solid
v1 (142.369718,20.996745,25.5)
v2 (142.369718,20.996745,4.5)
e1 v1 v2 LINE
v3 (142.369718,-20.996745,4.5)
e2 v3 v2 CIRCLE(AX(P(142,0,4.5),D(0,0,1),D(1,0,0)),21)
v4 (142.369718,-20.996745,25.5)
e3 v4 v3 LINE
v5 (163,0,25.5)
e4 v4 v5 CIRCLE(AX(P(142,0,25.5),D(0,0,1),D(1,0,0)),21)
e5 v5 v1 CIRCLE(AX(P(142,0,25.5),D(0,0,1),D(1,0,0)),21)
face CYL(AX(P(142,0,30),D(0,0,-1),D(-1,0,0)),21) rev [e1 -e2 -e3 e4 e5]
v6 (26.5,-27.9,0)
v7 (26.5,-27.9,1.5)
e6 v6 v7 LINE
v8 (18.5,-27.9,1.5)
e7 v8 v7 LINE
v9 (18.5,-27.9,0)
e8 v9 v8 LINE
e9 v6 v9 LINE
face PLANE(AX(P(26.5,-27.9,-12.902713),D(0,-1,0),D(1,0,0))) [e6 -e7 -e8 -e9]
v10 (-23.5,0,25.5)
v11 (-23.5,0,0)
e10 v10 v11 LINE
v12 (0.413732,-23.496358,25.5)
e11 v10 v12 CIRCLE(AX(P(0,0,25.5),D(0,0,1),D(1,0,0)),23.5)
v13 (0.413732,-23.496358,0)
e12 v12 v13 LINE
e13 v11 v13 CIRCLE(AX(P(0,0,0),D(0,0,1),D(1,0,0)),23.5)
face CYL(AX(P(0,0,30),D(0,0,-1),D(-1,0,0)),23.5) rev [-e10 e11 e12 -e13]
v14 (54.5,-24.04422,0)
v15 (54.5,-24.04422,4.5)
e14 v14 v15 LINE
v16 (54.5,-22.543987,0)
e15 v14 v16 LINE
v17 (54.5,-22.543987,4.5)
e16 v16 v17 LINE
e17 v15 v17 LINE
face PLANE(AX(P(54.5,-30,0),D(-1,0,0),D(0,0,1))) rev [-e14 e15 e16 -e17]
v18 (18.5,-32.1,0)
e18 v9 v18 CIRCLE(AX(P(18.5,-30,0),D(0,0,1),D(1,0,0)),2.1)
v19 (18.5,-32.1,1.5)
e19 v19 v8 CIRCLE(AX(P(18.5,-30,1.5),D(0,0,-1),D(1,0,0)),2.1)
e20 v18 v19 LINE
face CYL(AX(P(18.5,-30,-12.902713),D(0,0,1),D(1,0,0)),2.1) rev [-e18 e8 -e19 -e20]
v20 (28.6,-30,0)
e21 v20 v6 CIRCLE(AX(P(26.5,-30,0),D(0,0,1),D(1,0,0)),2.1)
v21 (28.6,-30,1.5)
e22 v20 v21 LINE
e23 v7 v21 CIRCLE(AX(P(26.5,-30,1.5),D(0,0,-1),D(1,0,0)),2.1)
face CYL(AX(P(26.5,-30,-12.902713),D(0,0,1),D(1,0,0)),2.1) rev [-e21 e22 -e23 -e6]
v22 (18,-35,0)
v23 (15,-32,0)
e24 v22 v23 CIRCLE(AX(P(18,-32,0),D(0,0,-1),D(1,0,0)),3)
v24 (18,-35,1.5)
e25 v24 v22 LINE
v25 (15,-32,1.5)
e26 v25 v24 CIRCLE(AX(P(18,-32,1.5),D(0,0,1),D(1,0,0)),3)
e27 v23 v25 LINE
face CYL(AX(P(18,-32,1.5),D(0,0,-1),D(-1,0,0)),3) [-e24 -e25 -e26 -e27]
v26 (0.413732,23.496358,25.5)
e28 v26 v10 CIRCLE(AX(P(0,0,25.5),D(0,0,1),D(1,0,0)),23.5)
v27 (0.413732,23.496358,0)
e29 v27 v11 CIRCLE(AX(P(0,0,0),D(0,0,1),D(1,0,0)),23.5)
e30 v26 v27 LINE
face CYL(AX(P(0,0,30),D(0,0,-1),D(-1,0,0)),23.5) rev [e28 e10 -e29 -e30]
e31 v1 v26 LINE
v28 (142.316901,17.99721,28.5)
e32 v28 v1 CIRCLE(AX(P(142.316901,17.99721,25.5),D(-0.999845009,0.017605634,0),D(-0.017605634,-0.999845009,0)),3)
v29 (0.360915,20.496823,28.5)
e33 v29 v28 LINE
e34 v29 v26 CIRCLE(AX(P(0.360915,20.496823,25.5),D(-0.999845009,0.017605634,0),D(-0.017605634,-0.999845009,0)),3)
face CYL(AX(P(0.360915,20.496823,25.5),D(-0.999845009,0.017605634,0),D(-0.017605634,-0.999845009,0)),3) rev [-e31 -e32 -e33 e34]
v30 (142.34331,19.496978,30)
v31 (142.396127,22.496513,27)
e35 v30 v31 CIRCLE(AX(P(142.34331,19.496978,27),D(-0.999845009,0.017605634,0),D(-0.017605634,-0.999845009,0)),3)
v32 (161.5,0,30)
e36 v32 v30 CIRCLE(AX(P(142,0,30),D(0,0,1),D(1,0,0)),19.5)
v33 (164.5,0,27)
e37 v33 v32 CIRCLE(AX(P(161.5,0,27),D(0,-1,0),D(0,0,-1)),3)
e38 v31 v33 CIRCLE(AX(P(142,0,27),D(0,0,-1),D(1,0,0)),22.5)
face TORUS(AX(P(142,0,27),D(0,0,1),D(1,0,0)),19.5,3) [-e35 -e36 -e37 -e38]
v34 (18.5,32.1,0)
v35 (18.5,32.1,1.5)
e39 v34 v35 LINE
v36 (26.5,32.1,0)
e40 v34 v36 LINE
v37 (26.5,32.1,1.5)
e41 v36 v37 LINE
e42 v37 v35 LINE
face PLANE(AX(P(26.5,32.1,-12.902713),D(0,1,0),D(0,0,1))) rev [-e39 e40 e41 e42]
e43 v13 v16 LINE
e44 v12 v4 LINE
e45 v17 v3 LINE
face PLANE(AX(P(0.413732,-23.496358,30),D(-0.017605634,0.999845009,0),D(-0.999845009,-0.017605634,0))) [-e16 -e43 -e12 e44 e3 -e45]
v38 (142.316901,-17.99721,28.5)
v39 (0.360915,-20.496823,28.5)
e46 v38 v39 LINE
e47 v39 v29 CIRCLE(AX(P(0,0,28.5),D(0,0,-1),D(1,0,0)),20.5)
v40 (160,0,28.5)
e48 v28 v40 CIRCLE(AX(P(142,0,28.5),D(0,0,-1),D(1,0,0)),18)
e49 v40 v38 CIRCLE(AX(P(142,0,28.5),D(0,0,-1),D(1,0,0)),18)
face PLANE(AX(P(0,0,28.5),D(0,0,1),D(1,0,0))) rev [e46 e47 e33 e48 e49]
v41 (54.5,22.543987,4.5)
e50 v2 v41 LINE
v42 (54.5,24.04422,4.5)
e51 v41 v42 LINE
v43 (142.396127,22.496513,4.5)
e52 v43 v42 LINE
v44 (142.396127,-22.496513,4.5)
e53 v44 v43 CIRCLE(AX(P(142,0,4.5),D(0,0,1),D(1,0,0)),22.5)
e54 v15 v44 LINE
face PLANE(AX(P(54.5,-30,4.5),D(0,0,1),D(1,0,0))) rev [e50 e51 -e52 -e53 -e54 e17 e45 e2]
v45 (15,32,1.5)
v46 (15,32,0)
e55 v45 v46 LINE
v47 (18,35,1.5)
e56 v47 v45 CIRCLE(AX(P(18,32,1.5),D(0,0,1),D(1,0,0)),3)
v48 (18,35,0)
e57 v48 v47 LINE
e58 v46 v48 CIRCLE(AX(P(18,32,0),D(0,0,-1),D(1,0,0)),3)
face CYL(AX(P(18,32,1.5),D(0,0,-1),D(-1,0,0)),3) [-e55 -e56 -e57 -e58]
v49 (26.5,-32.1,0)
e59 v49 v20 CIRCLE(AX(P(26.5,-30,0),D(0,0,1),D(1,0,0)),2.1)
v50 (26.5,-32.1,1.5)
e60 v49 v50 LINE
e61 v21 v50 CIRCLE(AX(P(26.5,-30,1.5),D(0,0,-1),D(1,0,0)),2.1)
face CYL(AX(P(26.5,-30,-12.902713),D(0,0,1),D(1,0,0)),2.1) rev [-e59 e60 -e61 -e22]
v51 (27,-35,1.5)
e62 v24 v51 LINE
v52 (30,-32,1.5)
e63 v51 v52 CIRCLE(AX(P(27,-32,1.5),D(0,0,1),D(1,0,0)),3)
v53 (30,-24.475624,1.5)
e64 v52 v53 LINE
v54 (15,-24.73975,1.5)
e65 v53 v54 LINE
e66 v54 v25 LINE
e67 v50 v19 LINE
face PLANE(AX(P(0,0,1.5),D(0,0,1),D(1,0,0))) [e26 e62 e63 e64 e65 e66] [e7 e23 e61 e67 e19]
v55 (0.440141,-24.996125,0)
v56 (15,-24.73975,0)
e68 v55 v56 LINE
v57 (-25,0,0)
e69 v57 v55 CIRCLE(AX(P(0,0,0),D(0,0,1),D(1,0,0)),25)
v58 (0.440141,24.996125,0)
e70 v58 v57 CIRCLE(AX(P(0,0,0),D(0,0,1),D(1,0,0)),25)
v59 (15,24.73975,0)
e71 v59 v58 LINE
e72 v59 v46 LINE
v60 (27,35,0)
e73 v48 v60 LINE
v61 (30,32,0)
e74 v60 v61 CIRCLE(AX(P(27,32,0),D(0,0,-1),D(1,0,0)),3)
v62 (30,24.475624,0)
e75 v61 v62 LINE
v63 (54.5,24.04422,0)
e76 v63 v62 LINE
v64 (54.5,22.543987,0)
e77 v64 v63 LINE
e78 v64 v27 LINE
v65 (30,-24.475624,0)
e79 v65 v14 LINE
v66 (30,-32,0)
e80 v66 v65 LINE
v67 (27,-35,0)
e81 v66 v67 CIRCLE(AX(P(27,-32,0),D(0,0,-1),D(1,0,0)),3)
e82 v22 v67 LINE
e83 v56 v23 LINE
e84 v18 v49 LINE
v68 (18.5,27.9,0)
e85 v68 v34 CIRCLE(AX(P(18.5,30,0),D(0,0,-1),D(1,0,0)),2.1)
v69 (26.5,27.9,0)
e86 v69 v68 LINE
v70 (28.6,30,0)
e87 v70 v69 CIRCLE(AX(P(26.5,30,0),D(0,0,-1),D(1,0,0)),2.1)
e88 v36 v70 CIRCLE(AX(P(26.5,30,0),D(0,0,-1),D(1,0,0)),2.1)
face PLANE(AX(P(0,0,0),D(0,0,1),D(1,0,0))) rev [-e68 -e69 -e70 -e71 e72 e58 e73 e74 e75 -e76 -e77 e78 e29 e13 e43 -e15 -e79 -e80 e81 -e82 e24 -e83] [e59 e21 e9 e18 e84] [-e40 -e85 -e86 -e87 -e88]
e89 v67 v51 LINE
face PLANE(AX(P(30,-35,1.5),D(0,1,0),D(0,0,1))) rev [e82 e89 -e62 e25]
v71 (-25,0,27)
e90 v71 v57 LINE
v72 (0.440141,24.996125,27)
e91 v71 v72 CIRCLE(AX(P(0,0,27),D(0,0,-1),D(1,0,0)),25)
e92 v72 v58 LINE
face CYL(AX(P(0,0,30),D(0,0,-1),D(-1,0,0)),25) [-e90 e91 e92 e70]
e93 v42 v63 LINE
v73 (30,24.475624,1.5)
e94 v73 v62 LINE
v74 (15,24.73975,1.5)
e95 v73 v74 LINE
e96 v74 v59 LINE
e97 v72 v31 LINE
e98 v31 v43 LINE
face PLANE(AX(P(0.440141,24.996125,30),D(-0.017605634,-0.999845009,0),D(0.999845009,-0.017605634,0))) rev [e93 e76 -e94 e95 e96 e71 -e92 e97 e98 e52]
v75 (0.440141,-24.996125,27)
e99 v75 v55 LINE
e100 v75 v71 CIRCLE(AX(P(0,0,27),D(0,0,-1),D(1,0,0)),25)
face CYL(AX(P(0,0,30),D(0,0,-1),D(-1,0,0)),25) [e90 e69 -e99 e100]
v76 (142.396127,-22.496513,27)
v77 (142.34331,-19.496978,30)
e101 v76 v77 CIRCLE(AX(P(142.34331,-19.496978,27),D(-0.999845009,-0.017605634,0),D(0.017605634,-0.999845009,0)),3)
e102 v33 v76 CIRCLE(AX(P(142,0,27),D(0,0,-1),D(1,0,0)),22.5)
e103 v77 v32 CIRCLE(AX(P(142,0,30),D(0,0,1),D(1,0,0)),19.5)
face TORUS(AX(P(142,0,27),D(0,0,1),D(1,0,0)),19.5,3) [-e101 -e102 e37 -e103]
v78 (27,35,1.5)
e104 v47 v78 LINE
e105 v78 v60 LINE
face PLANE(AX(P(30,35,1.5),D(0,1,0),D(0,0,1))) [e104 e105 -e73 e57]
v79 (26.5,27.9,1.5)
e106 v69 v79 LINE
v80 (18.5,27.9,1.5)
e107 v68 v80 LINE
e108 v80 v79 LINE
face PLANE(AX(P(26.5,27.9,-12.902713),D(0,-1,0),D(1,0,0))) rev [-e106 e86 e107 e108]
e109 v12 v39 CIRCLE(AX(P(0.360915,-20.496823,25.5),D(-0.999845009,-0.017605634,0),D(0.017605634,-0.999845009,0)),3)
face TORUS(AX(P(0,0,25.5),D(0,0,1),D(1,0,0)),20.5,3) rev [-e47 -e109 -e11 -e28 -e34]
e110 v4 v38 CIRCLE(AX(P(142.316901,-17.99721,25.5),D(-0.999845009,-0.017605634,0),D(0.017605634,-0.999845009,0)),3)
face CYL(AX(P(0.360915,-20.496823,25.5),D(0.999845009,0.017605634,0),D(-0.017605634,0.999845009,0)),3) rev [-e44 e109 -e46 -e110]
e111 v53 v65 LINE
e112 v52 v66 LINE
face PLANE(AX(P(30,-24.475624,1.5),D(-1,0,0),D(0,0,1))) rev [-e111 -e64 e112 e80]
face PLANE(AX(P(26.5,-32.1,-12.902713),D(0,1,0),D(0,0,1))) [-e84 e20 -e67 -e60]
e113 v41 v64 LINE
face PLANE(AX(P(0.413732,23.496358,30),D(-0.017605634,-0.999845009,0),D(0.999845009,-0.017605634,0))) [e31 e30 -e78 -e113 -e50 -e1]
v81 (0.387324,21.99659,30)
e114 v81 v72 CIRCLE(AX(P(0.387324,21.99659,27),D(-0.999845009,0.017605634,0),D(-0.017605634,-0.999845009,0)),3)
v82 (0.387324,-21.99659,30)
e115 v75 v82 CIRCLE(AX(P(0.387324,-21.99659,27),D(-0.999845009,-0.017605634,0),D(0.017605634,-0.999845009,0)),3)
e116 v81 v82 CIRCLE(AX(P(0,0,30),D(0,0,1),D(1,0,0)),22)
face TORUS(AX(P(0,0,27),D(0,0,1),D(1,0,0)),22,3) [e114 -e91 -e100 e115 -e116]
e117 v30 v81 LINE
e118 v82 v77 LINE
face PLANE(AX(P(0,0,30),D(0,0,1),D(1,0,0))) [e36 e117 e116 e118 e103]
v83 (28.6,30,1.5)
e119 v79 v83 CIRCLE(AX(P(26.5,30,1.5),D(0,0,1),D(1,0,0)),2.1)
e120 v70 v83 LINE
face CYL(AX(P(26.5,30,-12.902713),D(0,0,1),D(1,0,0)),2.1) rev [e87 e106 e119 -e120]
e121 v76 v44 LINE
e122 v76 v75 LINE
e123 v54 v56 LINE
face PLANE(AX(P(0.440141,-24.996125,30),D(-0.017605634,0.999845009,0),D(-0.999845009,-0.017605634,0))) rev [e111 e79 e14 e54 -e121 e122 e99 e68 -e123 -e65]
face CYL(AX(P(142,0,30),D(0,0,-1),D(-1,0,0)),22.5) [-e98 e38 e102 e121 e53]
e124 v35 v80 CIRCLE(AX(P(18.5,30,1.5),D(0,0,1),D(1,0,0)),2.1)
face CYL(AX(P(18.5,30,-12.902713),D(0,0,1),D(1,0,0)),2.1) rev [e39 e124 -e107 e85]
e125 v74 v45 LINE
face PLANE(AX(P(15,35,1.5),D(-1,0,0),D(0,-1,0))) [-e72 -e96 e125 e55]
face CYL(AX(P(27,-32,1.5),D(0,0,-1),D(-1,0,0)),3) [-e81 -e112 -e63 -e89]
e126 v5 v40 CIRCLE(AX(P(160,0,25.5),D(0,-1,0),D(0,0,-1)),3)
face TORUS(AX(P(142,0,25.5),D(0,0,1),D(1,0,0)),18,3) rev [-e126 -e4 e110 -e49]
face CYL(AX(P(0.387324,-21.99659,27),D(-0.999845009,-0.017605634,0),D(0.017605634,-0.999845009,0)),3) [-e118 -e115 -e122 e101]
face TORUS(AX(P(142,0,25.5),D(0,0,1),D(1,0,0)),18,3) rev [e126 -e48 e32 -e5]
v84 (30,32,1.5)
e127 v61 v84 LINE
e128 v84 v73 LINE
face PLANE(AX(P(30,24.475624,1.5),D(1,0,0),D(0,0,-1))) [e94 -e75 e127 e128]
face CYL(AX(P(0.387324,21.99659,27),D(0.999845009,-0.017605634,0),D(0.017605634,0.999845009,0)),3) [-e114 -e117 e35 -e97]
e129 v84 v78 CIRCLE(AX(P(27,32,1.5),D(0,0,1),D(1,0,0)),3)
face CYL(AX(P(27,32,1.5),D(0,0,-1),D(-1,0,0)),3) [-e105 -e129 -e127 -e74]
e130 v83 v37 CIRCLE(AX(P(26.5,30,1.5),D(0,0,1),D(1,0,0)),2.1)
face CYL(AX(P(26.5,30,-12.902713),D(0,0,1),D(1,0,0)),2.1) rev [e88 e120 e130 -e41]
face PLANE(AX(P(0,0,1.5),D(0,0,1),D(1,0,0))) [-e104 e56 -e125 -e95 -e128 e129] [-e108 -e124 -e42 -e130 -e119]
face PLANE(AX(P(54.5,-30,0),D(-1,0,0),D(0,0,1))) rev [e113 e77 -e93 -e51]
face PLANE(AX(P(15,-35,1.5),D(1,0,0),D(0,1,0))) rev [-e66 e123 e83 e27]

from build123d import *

# Parameters (mm, degrees)
EXTRUDE_1_DEPTH     = 30
SHELL_1_T           = -1.5
EXTRUDE_2_DEPTH     = 1.5
CUT_EXTRUDE_1_DEPTH = 1.5
FILLET_1_R          = 3
SKETCH_4_W          = 110
SKETCH_4_H          = 4.5
CUT_EXTRUDE_2_DEPTH = 30


with BuildPart() as part:
    # 草图1 → 凸台-拉伸1 (new body)
    with BuildSketch(Plane.XY):
        with BuildLine():
            Line((0.440140845, 24.99612522), (142.396126761, 22.496512698))
            ThreePointArc((142.396126761, 22.496512698), (164.5, 0), (142.396126761, -22.496512698))
            Line((142.396126761, -22.496512698), (0.440140845, -24.99612522))
            ThreePointArc((0.440140845, -24.99612522), (-25, 0), (0.440140845, 24.99612522))
        make_face()
    extrude(amount=EXTRUDE_1_DEPTH)

    # 抽壳1
    shell_1_openings = [part.faces().sort_by_distance(p)[0] for p in [
        (68.129004911, 0, 0),
    ]]
    offset(amount=SHELL_1_T, openings=shell_1_openings, kind=Kind.INTERSECTION)

    # 草图2 → 凸台-拉伸2 (add)
    with BuildSketch(Plane(origin=(0, 0, 0), x_dir=(-1, 0, 0), z_dir=(0, 0, -1))):
        Polygon((-30, 24.475624492), (-30, 35), (-15, 35), (-15, 24.739749936), align=None)
    extrude_2 = extrude(amount=-EXTRUDE_2_DEPTH)

    # 草图3 → 切除-拉伸1 (cut)
    with BuildSketch(Plane.XY.offset(1.5)):
        with BuildLine():
            Line((26.5, 27.9), (18.5, 27.9))
            ThreePointArc((18.5, 27.9), (16.4, 30), (18.5, 32.1))
            Line((18.5, 32.1), (26.5, 32.1))
            ThreePointArc((26.5, 32.1), (28.6, 30), (26.5, 27.9))
        make_face()
    cut_extrude_1 = extrude(amount=-CUT_EXTRUDE_1_DEPTH, mode=Mode.SUBTRACT)

    # 镜向1: 凸台-拉伸2, 切除-拉伸1 across plane
    add(extrude_2.mirror(Plane.ZX))
    add(cut_extrude_1.mirror(Plane.ZX), mode=Mode.SUBTRACT)

    # 圆角1
    fillet_1_edges = [part.edges().sort_by_distance(p)[0] for p in [
        (164.5, 0, 30),
        (71.418133803, 23.746318959, 30),
        (-23.5, 0, 28.5),
        (71.391725352, -22.246551446, 28.5),
        (163, 0, 28.5),
        (71.391725352, 22.246551446, 28.5),
        (30, 35, 0.75),
        (15, 35, 0.75),
        (-25, 0, 30),
        (15, -35, 0.75),
        (30, -35, 0.75),
        (71.418133803, -23.746318959, 30),
    ]]
    fillet(fillet_1_edges, radius=FILLET_1_R)

    # 草图4 → 切除-拉伸2 (cut, symmetric)
    with BuildSketch(Plane(origin=(0, 0, 0), x_dir=(1, 0, 0), z_dir=(0, 1, 0))):
        with Locations((109.5, -2.25)):
            Rectangle(SKETCH_4_W, SKETCH_4_H)
    extrude(amount=CUT_EXTRUDE_2_DEPTH, both=True, mode=Mode.SUBTRACT)


solid = part.part
